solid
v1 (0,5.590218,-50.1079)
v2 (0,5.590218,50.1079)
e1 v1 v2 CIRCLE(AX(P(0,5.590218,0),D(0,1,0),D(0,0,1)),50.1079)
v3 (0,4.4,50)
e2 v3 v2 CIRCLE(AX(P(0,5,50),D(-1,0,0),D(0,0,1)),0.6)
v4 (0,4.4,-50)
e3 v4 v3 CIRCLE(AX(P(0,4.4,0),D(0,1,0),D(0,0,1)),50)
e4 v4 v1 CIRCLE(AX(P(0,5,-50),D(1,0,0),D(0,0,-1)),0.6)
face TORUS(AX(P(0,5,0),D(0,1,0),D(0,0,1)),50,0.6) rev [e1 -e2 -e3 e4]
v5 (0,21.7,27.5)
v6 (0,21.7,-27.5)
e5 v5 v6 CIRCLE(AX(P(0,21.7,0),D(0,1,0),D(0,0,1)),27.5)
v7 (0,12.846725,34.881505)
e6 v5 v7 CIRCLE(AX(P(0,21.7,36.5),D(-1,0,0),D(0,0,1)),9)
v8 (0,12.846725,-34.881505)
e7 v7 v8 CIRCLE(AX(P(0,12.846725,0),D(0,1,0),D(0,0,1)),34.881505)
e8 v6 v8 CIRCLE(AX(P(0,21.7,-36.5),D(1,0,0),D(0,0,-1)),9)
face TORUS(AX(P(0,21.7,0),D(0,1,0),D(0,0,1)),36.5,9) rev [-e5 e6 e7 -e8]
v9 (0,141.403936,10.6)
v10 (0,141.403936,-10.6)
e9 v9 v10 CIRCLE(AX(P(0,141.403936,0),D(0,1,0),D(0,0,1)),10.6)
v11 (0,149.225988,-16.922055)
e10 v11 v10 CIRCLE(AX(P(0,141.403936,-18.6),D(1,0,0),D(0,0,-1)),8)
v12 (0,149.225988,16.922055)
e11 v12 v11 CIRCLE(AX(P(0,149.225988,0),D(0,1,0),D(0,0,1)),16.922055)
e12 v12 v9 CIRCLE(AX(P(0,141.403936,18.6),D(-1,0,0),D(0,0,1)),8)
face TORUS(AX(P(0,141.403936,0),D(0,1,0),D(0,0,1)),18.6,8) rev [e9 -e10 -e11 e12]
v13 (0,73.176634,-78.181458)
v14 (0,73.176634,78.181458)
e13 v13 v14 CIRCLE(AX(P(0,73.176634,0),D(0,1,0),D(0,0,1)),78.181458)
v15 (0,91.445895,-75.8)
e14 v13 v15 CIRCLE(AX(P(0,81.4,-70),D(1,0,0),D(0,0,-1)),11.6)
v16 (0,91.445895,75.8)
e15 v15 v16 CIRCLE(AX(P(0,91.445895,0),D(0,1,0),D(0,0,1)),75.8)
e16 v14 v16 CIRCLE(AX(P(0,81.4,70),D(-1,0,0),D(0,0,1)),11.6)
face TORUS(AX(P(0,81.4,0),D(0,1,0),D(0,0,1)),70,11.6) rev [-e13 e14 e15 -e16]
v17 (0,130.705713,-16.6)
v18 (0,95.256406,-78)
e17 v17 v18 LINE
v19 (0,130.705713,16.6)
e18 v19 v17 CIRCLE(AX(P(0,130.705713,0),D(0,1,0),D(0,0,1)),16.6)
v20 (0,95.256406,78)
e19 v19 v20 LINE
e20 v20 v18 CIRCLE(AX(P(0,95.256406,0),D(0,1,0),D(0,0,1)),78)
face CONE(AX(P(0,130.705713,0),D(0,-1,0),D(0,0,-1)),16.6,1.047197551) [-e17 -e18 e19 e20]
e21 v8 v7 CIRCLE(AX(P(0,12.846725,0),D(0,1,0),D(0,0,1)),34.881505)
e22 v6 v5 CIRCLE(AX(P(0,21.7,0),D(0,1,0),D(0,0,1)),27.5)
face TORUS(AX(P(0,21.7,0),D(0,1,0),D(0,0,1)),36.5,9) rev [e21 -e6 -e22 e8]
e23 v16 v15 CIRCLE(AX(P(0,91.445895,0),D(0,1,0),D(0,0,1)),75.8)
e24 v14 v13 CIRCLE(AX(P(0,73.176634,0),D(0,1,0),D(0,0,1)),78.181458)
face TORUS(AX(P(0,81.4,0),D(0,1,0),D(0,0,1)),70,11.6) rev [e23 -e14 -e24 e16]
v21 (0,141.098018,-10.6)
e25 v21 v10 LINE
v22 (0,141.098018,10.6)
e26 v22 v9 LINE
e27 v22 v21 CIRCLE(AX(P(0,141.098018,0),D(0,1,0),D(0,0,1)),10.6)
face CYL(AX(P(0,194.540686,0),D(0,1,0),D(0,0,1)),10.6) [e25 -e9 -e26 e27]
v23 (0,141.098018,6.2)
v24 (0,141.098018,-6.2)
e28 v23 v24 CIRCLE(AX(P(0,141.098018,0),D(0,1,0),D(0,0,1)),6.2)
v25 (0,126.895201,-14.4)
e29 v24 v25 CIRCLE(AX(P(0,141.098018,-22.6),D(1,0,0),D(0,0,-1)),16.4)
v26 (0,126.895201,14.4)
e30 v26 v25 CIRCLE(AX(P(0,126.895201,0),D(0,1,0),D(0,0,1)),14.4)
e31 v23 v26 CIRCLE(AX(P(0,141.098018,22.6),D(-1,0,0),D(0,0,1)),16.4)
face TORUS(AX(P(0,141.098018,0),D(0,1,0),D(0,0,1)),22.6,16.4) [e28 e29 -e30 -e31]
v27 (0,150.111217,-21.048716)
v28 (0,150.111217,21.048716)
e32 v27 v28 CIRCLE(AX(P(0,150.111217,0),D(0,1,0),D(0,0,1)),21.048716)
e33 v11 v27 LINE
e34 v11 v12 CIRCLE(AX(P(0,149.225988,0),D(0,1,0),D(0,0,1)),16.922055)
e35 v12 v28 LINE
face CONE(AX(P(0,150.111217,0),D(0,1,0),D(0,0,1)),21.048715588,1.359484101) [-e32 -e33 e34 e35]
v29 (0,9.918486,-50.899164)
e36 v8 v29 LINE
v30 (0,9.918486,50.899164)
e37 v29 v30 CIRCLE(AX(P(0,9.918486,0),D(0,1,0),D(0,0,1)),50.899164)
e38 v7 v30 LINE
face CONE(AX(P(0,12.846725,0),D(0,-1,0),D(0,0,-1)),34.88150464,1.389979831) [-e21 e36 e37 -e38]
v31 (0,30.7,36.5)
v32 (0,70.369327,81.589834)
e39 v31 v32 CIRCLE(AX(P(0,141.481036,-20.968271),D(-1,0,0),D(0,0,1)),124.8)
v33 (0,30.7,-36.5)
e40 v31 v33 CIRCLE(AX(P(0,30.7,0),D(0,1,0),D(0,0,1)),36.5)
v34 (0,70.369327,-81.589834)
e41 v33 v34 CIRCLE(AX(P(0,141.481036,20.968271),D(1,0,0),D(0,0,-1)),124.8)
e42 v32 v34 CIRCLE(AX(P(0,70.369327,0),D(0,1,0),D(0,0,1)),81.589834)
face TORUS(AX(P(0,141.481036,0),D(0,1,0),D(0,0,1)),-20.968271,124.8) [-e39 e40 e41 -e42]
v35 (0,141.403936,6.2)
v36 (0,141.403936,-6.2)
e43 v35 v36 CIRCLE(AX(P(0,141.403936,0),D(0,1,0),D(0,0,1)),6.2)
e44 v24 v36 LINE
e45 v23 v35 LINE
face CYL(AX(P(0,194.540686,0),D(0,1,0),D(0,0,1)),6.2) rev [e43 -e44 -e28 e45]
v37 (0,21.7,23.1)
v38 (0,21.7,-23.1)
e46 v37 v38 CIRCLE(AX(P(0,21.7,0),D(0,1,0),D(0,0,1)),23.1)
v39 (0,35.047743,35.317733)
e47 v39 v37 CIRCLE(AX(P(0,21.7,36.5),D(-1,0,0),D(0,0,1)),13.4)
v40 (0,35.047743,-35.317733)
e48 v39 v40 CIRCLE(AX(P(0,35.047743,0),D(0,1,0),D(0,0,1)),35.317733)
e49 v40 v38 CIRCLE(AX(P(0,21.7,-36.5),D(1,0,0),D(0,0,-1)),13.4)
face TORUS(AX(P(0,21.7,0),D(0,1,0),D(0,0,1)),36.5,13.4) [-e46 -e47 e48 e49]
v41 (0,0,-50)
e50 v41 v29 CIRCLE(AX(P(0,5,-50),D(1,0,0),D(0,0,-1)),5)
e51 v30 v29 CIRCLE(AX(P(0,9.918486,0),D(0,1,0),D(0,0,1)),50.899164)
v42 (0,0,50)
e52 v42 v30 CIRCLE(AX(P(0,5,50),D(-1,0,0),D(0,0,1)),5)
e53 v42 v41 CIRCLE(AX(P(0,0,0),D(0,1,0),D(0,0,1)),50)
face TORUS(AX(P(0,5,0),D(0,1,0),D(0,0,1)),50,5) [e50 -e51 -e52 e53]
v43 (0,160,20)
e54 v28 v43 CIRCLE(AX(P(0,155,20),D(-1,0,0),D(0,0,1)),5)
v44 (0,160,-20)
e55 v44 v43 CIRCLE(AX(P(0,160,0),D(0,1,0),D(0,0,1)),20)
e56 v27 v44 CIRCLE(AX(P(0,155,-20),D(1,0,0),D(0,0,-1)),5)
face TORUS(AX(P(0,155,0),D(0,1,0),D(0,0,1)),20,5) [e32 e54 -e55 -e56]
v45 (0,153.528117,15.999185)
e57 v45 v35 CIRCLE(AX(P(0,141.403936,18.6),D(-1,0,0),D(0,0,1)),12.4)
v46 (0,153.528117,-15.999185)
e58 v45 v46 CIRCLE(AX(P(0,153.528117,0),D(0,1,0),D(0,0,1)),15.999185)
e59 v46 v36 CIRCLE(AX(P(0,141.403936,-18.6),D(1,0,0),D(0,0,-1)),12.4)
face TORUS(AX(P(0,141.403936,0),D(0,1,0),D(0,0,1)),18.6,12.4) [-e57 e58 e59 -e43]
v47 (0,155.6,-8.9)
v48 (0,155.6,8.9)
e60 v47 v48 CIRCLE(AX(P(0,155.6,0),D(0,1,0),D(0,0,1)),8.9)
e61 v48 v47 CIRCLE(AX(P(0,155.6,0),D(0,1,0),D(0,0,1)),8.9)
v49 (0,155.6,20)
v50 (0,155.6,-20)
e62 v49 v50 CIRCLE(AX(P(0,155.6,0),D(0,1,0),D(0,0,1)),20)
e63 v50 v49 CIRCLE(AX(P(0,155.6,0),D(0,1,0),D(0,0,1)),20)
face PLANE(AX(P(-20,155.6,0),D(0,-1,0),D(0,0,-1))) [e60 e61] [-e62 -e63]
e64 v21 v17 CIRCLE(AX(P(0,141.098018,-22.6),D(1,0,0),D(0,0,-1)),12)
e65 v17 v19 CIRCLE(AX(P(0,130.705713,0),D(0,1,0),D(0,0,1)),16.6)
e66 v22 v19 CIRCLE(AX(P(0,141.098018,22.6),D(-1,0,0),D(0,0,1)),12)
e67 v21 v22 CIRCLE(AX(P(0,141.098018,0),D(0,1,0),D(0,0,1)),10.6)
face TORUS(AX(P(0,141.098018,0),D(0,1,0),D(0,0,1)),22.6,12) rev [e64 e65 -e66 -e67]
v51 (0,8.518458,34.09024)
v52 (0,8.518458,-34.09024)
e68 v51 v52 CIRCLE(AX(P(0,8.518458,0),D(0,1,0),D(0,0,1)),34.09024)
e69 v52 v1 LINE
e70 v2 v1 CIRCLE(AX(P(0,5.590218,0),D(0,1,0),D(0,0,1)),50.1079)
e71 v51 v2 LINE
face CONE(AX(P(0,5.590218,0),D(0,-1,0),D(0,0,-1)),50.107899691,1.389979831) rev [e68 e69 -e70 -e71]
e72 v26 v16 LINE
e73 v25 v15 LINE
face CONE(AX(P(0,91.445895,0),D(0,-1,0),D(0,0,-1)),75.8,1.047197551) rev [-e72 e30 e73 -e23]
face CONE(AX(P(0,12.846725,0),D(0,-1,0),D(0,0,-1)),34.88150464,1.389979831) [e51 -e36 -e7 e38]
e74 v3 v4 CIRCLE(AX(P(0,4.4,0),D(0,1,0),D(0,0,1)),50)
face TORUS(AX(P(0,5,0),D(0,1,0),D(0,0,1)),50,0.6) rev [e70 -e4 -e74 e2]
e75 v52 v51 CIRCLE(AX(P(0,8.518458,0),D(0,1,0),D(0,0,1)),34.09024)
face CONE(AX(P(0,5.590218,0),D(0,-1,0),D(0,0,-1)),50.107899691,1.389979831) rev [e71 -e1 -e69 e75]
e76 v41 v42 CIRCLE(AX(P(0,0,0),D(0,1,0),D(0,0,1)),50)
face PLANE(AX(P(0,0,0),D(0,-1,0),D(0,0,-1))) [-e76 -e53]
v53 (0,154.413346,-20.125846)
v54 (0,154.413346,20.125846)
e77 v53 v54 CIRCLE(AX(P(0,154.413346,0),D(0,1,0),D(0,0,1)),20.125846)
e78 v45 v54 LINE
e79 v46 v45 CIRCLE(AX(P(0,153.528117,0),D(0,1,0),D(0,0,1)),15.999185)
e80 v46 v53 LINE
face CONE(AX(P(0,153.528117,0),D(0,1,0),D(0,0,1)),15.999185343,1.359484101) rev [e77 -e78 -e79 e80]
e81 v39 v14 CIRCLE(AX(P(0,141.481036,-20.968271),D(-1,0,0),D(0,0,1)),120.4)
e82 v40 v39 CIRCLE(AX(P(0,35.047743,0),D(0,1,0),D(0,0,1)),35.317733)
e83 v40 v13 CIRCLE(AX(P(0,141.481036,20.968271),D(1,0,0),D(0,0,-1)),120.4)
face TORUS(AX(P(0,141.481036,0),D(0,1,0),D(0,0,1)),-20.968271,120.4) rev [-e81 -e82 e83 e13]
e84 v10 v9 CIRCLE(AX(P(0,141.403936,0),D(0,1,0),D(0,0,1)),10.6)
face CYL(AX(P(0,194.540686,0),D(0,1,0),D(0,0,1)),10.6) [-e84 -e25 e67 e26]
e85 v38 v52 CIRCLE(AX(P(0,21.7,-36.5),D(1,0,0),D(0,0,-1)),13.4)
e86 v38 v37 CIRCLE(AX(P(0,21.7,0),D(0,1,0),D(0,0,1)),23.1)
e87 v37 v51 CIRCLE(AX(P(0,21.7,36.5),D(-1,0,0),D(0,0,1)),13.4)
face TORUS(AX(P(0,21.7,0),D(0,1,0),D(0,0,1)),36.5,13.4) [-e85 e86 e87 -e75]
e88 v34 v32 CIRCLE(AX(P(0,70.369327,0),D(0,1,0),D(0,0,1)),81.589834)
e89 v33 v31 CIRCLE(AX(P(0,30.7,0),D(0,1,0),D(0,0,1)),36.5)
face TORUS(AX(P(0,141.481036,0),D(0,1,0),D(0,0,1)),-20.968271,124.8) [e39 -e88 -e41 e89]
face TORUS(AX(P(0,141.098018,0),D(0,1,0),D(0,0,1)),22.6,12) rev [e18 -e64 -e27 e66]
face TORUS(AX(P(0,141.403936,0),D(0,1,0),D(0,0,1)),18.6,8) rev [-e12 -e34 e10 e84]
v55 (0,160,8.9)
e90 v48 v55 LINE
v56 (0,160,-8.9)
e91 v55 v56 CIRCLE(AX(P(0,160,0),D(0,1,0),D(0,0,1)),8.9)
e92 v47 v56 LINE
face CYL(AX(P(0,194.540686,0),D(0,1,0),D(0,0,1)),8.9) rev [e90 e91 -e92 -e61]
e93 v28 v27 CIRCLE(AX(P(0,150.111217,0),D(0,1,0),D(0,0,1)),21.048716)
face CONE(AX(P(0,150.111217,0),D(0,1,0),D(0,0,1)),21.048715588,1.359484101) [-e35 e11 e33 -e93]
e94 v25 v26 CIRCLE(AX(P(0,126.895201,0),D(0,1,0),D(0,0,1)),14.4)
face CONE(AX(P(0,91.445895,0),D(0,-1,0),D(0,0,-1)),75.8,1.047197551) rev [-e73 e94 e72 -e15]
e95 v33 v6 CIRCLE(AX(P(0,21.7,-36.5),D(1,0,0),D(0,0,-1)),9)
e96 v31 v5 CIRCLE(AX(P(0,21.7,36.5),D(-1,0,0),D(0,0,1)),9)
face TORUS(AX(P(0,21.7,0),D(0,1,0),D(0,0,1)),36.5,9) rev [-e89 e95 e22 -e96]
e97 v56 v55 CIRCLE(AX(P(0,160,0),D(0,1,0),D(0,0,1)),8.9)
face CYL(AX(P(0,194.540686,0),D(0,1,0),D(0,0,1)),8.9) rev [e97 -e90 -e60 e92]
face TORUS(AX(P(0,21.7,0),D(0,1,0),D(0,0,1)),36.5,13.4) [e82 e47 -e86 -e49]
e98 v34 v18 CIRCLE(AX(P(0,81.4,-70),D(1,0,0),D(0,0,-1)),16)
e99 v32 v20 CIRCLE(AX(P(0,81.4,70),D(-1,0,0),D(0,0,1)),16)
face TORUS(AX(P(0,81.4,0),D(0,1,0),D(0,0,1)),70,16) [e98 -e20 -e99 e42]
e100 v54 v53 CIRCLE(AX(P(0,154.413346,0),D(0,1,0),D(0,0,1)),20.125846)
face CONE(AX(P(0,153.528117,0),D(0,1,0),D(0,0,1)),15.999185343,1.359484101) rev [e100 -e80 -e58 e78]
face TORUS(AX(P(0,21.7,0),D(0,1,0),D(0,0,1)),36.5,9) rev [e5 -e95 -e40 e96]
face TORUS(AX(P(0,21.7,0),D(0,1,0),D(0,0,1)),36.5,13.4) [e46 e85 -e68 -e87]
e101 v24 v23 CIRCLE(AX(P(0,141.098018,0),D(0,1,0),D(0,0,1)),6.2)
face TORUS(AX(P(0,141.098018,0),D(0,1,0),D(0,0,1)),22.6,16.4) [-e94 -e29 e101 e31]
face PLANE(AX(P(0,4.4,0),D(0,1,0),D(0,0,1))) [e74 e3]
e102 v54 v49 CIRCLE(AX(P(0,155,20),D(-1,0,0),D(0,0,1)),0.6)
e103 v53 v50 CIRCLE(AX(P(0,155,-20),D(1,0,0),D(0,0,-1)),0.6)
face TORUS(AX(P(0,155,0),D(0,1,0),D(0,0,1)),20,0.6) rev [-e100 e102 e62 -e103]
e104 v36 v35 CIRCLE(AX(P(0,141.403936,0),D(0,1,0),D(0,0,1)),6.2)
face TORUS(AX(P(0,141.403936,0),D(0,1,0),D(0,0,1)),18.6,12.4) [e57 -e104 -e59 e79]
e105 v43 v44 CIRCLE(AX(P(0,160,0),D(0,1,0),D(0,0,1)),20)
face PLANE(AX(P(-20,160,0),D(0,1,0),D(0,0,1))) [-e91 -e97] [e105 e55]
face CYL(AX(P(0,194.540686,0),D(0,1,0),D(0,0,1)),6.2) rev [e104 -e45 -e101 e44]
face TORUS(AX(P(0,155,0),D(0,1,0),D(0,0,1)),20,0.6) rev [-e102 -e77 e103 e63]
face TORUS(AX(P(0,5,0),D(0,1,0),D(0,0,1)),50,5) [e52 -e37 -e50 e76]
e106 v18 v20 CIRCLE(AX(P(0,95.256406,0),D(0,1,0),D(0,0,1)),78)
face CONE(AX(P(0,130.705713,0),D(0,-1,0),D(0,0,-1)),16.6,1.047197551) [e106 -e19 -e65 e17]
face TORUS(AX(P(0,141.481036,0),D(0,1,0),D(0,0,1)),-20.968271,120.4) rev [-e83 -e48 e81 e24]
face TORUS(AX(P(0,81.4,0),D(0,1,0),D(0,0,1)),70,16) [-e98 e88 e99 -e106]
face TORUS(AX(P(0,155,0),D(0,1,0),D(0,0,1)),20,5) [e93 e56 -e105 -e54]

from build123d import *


with BuildPart() as part:
    # Jar Profile Sketch → Jar Body Revolve 360° (revolve)
    with BuildSketch(Plane.XY, mode=Mode.PRIVATE) as jar_body_revolve_360_sk:
        with BuildLine():
            Line((0, 0), (-50, 0))
            ThreePointArc((-50, 0), (-54.979579786, 4.548574314), (-50.899164089, 9.91848594))
            Line((-50.899164089, 9.91848594), (-34.88150464, 12.846725308))
            ThreePointArc((-34.88150464, 12.846725308), (-27.536756384, 22.512566235), (-36.5, 30.7))
            ThreePointArc((-36.5, 30.7), (-61.466698286, 47.781964835), (-81.589834313, 70.369327283))
            ThreePointArc((-81.589834313, 70.369327283), (-85.836100518, 83.684276777), (-78, 95.256406461))
            Line((-78, 95.256406461), (-16.6, 130.705712989))
            ThreePointArc((-16.6, 130.705712989), (-12.207695155, 135.098017834), (-10.6, 141.098017834))
            Line((-10.6, 141.098017834), (-10.6, 141.403935942))
            ThreePointArc((-10.6, 141.403935942), (-12.378120882, 146.43267537), (-16.92205506, 149.225988152))
            Line((-16.92205506, 149.225988152), (-21.048715588, 150.111217369))
            ThreePointArc((-21.048715588, 150.111217369), (-24.972117917, 155.527298228), (-20, 160))
            Line((-20, 160), (-8.9, 160))
            Line((-8.9, 160), (-8.9, 155.6))
            Line((-8.9, 155.6), (-20, 155.6))
            ThreePointArc((-20, 155.6), (-20.59665415, 155.063275787), (-20.125845871, 154.413346084))
            Line((-20.125845871, 154.413346084), (-15.999185343, 153.528116868))
            ThreePointArc((-15.999185343, 153.528116868), (-8.956087367, 149.198482056), (-6.2, 141.403935942))
            Line((-6.2, 141.403935942), (-6.2, 141.098017834))
            ThreePointArc((-6.2, 141.098017834), (-8.397183378, 132.898017834), (-14.4, 126.895201212))
            Line((-14.4, 126.895201212), (-75.8, 91.445894684))
            ThreePointArc((-75.8, 91.445894684), (-81.502684952, 82.899412851), (-78.181458219, 73.176634423))
            ThreePointArc((-78.181458219, 73.176634423), (-59.053725287, 51.521933043), (-35.317733129, 35.047743069))
            ThreePointArc((-35.317733129, 35.047743069), (-23.114320726, 22.319346728), (-34.090240242, 8.518457681))
            Line((-34.090240242, 8.518457681), (-50.107899691, 5.590218313))
            ThreePointArc((-50.107899691, 5.590218313), (-50.597549574, 4.945828918), (-50, 4.4))
            Line((-50, 4.4), (0, 4.4))
            Line((0, 4.4), (0, 0))
        make_face()
    revolve(jar_body_revolve_360_sk.sketch.rotate(Axis((0, 194.540686074, 0), (0, -1, 0)), 270), axis=Axis((0, 194.540686074, 0), (0, -1, 0)))


solid = part.part
